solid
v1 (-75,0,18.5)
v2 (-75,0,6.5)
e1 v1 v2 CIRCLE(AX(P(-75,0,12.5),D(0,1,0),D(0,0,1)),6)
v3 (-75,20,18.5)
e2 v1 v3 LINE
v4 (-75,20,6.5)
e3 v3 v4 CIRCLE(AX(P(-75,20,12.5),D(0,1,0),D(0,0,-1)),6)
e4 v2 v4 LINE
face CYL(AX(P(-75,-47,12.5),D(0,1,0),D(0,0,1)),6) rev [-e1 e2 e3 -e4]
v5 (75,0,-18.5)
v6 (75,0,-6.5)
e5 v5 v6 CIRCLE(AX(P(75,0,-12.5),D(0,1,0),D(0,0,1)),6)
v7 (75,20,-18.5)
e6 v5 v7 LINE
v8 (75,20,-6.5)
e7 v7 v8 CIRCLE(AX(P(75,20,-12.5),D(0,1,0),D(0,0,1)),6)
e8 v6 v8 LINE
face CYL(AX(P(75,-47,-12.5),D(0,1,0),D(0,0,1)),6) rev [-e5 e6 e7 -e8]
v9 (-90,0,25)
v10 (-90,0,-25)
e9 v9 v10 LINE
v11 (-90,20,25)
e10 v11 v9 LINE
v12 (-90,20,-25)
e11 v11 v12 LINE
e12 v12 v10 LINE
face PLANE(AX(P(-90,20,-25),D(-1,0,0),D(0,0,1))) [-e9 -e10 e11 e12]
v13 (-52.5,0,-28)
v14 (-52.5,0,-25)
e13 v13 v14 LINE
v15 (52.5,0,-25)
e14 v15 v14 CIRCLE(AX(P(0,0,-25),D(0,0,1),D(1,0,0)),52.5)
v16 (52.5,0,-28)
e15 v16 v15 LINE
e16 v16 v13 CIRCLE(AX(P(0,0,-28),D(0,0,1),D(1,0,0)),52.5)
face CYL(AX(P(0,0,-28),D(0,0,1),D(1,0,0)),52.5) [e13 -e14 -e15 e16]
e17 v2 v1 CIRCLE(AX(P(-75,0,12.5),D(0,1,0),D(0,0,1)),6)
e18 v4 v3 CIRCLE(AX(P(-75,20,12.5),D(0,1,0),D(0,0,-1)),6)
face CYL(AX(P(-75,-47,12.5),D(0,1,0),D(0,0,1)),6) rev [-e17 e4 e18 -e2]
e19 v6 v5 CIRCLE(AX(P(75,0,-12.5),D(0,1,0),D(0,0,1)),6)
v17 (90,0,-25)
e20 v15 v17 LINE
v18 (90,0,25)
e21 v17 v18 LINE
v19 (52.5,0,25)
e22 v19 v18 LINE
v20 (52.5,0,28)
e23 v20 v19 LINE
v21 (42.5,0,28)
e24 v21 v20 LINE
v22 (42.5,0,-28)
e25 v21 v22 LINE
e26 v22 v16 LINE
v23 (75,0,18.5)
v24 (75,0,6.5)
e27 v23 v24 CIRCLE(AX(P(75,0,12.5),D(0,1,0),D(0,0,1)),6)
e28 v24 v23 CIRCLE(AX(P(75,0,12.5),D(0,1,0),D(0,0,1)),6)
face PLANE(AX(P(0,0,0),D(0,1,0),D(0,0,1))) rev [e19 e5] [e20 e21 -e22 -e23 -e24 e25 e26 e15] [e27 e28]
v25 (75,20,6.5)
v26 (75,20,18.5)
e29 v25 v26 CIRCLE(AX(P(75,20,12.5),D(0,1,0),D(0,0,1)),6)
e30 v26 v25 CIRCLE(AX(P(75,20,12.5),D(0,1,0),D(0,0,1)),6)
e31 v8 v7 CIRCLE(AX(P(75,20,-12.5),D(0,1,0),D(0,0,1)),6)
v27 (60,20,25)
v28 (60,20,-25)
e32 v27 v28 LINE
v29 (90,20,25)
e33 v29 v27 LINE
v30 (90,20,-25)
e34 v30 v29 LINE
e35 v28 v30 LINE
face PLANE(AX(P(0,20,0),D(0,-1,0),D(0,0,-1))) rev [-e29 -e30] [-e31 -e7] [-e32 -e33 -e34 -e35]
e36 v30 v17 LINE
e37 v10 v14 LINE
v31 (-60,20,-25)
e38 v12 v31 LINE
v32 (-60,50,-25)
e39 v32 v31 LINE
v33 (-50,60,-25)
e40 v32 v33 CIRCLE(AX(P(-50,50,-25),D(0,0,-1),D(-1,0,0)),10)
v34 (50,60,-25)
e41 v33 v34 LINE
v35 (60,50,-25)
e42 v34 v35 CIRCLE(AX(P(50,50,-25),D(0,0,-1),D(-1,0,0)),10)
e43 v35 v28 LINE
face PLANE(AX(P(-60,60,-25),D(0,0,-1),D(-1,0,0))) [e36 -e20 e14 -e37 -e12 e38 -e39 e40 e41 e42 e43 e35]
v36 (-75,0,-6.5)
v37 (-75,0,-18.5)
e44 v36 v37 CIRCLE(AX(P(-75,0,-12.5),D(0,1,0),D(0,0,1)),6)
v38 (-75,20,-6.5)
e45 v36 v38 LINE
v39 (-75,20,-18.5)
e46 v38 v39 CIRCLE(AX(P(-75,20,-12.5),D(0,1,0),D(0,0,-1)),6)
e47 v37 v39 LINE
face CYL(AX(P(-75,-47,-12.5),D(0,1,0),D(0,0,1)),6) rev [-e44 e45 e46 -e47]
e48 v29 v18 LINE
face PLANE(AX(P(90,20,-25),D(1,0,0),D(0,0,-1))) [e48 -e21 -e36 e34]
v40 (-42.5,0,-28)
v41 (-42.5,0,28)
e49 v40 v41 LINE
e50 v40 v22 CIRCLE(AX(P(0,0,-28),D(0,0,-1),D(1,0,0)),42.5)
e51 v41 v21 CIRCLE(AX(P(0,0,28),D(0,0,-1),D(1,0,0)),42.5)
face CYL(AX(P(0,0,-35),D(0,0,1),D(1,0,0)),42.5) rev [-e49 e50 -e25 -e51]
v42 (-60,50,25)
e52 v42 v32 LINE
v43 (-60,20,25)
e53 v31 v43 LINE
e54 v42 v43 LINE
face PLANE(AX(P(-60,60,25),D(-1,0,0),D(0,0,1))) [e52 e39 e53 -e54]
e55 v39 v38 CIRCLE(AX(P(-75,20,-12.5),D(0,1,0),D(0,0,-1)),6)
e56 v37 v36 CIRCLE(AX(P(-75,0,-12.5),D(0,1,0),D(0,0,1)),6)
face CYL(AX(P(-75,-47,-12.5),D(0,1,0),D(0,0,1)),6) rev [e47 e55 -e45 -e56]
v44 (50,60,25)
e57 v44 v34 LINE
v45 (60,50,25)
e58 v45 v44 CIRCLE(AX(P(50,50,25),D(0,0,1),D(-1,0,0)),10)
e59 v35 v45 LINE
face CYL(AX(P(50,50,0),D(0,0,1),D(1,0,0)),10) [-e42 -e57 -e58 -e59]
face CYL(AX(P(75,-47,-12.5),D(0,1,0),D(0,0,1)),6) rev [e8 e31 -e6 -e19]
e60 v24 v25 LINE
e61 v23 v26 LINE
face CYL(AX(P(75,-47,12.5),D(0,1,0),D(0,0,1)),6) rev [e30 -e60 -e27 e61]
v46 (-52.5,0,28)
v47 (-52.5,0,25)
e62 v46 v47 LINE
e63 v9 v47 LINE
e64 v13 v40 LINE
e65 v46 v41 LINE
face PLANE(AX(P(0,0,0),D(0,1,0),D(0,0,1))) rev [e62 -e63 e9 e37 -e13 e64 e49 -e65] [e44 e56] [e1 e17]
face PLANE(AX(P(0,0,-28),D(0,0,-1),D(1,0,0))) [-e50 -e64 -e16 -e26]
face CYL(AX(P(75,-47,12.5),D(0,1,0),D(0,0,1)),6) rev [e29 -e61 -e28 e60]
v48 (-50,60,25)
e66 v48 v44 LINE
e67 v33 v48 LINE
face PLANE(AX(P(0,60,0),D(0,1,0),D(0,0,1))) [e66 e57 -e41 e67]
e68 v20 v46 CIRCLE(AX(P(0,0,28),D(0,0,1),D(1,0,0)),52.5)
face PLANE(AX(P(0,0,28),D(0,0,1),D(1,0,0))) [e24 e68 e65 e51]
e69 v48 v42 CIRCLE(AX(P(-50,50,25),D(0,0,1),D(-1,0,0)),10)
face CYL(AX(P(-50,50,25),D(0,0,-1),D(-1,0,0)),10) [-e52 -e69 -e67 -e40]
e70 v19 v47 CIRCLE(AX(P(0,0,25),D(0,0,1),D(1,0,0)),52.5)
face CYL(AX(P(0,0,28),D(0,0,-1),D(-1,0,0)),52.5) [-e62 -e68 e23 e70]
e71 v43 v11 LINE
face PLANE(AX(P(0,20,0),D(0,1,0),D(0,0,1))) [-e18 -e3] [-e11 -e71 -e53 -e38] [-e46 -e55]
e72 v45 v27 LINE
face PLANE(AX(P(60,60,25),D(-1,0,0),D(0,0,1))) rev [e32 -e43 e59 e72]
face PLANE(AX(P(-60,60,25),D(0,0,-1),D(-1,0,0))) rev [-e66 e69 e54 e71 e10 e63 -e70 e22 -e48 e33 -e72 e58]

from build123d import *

# Parameters (mm, degrees)
SKETCH_1_W          = 120
SKETCH_1_H          = 50
EXTRUDE_1_DEPTH     = 60
SKETCH_2_R          = 42.5
CUT_EXTRUDE_1_DEPTH = 60
SKETCH_3_W          = 30
SKETCH_3_H          = 50
EXTRUDE_2_DEPTH     = 20
FILLET_1_R          = 10
EXTRUDE_START       = 3
EXTRUDE_3_DEPTH     = 3
SKETCH_5_R          = 6
CUT_EXTRUDE_2_DEPTH = 67


with BuildPart() as part:
    # 草图1 → 凸台-拉伸1 (new body)
    with BuildSketch(Plane(origin=(0, 0, 0), x_dir=(1, 0, 0), z_dir=(0, 1, 0))):
        Rectangle(SKETCH_1_W, SKETCH_1_H)
    extrude(amount=EXTRUDE_1_DEPTH)

    # 草图2 → 切除-拉伸1 (cut)
    with BuildSketch(Plane.XY.offset(25)):
        Circle(SKETCH_2_R)
    extrude(amount=-CUT_EXTRUDE_1_DEPTH, mode=Mode.SUBTRACT)

    # 草图3 → 凸台-拉伸2 (add)
    with BuildSketch(Plane.XZ):
        with Locations((-75, 0)):
            Rectangle(SKETCH_3_W, SKETCH_3_H)
        with Locations((75, 0)):
            Rectangle(SKETCH_3_W, SKETCH_3_H)
    extrude(amount=-EXTRUDE_2_DEPTH)

    # 圆角1
    fillet_1_edges = [part.edges().sort_by_distance(p)[0] for p in [
        (-60, 60, 0),
        (60, 60, 0),
    ]]
    fillet(fillet_1_edges, radius=FILLET_1_R)

    # 草图4 → 凸台-拉伸3 (add)
    with BuildSketch(Plane.XY.offset(25).offset(EXTRUDE_START)):
        with BuildLine():
            Line((-52.5, 0), (-42.5, 0))
            ThreePointArc((-42.5, 0), (0, 42.5), (42.5, 0))
            Line((42.5, 0), (52.5, 0))
            ThreePointArc((52.5, 0), (0, 52.5), (-52.5, 0))
        make_face()
    extrude_3 = extrude(amount=-EXTRUDE_3_DEPTH)

    # 镜向1: 凸台-拉伸3 across plane
    add(extrude_3.mirror(Plane.XY))

    # 草图5 → 切除-拉伸2 (cut)
    with BuildSketch(Plane(origin=(0, 20, 0), x_dir=(1, 0, 0), z_dir=(0, 1, 0))):
        with Locations(Location((75, 12.5, 0), (0, 0, 270))):
            Circle(SKETCH_5_R)
        with Locations(Location((75, -12.5, 0), (0, 0, 270))):
            Circle(SKETCH_5_R)
        with Locations(Location((-75, -12.5, 0), (0, 0, 270))):
            Circle(SKETCH_5_R)
        with Locations(Location((-75, 12.5, 0), (0, 0, 270))):
            Circle(SKETCH_5_R)
    extrude(amount=-CUT_EXTRUDE_2_DEPTH, mode=Mode.SUBTRACT)


solid = part.part
